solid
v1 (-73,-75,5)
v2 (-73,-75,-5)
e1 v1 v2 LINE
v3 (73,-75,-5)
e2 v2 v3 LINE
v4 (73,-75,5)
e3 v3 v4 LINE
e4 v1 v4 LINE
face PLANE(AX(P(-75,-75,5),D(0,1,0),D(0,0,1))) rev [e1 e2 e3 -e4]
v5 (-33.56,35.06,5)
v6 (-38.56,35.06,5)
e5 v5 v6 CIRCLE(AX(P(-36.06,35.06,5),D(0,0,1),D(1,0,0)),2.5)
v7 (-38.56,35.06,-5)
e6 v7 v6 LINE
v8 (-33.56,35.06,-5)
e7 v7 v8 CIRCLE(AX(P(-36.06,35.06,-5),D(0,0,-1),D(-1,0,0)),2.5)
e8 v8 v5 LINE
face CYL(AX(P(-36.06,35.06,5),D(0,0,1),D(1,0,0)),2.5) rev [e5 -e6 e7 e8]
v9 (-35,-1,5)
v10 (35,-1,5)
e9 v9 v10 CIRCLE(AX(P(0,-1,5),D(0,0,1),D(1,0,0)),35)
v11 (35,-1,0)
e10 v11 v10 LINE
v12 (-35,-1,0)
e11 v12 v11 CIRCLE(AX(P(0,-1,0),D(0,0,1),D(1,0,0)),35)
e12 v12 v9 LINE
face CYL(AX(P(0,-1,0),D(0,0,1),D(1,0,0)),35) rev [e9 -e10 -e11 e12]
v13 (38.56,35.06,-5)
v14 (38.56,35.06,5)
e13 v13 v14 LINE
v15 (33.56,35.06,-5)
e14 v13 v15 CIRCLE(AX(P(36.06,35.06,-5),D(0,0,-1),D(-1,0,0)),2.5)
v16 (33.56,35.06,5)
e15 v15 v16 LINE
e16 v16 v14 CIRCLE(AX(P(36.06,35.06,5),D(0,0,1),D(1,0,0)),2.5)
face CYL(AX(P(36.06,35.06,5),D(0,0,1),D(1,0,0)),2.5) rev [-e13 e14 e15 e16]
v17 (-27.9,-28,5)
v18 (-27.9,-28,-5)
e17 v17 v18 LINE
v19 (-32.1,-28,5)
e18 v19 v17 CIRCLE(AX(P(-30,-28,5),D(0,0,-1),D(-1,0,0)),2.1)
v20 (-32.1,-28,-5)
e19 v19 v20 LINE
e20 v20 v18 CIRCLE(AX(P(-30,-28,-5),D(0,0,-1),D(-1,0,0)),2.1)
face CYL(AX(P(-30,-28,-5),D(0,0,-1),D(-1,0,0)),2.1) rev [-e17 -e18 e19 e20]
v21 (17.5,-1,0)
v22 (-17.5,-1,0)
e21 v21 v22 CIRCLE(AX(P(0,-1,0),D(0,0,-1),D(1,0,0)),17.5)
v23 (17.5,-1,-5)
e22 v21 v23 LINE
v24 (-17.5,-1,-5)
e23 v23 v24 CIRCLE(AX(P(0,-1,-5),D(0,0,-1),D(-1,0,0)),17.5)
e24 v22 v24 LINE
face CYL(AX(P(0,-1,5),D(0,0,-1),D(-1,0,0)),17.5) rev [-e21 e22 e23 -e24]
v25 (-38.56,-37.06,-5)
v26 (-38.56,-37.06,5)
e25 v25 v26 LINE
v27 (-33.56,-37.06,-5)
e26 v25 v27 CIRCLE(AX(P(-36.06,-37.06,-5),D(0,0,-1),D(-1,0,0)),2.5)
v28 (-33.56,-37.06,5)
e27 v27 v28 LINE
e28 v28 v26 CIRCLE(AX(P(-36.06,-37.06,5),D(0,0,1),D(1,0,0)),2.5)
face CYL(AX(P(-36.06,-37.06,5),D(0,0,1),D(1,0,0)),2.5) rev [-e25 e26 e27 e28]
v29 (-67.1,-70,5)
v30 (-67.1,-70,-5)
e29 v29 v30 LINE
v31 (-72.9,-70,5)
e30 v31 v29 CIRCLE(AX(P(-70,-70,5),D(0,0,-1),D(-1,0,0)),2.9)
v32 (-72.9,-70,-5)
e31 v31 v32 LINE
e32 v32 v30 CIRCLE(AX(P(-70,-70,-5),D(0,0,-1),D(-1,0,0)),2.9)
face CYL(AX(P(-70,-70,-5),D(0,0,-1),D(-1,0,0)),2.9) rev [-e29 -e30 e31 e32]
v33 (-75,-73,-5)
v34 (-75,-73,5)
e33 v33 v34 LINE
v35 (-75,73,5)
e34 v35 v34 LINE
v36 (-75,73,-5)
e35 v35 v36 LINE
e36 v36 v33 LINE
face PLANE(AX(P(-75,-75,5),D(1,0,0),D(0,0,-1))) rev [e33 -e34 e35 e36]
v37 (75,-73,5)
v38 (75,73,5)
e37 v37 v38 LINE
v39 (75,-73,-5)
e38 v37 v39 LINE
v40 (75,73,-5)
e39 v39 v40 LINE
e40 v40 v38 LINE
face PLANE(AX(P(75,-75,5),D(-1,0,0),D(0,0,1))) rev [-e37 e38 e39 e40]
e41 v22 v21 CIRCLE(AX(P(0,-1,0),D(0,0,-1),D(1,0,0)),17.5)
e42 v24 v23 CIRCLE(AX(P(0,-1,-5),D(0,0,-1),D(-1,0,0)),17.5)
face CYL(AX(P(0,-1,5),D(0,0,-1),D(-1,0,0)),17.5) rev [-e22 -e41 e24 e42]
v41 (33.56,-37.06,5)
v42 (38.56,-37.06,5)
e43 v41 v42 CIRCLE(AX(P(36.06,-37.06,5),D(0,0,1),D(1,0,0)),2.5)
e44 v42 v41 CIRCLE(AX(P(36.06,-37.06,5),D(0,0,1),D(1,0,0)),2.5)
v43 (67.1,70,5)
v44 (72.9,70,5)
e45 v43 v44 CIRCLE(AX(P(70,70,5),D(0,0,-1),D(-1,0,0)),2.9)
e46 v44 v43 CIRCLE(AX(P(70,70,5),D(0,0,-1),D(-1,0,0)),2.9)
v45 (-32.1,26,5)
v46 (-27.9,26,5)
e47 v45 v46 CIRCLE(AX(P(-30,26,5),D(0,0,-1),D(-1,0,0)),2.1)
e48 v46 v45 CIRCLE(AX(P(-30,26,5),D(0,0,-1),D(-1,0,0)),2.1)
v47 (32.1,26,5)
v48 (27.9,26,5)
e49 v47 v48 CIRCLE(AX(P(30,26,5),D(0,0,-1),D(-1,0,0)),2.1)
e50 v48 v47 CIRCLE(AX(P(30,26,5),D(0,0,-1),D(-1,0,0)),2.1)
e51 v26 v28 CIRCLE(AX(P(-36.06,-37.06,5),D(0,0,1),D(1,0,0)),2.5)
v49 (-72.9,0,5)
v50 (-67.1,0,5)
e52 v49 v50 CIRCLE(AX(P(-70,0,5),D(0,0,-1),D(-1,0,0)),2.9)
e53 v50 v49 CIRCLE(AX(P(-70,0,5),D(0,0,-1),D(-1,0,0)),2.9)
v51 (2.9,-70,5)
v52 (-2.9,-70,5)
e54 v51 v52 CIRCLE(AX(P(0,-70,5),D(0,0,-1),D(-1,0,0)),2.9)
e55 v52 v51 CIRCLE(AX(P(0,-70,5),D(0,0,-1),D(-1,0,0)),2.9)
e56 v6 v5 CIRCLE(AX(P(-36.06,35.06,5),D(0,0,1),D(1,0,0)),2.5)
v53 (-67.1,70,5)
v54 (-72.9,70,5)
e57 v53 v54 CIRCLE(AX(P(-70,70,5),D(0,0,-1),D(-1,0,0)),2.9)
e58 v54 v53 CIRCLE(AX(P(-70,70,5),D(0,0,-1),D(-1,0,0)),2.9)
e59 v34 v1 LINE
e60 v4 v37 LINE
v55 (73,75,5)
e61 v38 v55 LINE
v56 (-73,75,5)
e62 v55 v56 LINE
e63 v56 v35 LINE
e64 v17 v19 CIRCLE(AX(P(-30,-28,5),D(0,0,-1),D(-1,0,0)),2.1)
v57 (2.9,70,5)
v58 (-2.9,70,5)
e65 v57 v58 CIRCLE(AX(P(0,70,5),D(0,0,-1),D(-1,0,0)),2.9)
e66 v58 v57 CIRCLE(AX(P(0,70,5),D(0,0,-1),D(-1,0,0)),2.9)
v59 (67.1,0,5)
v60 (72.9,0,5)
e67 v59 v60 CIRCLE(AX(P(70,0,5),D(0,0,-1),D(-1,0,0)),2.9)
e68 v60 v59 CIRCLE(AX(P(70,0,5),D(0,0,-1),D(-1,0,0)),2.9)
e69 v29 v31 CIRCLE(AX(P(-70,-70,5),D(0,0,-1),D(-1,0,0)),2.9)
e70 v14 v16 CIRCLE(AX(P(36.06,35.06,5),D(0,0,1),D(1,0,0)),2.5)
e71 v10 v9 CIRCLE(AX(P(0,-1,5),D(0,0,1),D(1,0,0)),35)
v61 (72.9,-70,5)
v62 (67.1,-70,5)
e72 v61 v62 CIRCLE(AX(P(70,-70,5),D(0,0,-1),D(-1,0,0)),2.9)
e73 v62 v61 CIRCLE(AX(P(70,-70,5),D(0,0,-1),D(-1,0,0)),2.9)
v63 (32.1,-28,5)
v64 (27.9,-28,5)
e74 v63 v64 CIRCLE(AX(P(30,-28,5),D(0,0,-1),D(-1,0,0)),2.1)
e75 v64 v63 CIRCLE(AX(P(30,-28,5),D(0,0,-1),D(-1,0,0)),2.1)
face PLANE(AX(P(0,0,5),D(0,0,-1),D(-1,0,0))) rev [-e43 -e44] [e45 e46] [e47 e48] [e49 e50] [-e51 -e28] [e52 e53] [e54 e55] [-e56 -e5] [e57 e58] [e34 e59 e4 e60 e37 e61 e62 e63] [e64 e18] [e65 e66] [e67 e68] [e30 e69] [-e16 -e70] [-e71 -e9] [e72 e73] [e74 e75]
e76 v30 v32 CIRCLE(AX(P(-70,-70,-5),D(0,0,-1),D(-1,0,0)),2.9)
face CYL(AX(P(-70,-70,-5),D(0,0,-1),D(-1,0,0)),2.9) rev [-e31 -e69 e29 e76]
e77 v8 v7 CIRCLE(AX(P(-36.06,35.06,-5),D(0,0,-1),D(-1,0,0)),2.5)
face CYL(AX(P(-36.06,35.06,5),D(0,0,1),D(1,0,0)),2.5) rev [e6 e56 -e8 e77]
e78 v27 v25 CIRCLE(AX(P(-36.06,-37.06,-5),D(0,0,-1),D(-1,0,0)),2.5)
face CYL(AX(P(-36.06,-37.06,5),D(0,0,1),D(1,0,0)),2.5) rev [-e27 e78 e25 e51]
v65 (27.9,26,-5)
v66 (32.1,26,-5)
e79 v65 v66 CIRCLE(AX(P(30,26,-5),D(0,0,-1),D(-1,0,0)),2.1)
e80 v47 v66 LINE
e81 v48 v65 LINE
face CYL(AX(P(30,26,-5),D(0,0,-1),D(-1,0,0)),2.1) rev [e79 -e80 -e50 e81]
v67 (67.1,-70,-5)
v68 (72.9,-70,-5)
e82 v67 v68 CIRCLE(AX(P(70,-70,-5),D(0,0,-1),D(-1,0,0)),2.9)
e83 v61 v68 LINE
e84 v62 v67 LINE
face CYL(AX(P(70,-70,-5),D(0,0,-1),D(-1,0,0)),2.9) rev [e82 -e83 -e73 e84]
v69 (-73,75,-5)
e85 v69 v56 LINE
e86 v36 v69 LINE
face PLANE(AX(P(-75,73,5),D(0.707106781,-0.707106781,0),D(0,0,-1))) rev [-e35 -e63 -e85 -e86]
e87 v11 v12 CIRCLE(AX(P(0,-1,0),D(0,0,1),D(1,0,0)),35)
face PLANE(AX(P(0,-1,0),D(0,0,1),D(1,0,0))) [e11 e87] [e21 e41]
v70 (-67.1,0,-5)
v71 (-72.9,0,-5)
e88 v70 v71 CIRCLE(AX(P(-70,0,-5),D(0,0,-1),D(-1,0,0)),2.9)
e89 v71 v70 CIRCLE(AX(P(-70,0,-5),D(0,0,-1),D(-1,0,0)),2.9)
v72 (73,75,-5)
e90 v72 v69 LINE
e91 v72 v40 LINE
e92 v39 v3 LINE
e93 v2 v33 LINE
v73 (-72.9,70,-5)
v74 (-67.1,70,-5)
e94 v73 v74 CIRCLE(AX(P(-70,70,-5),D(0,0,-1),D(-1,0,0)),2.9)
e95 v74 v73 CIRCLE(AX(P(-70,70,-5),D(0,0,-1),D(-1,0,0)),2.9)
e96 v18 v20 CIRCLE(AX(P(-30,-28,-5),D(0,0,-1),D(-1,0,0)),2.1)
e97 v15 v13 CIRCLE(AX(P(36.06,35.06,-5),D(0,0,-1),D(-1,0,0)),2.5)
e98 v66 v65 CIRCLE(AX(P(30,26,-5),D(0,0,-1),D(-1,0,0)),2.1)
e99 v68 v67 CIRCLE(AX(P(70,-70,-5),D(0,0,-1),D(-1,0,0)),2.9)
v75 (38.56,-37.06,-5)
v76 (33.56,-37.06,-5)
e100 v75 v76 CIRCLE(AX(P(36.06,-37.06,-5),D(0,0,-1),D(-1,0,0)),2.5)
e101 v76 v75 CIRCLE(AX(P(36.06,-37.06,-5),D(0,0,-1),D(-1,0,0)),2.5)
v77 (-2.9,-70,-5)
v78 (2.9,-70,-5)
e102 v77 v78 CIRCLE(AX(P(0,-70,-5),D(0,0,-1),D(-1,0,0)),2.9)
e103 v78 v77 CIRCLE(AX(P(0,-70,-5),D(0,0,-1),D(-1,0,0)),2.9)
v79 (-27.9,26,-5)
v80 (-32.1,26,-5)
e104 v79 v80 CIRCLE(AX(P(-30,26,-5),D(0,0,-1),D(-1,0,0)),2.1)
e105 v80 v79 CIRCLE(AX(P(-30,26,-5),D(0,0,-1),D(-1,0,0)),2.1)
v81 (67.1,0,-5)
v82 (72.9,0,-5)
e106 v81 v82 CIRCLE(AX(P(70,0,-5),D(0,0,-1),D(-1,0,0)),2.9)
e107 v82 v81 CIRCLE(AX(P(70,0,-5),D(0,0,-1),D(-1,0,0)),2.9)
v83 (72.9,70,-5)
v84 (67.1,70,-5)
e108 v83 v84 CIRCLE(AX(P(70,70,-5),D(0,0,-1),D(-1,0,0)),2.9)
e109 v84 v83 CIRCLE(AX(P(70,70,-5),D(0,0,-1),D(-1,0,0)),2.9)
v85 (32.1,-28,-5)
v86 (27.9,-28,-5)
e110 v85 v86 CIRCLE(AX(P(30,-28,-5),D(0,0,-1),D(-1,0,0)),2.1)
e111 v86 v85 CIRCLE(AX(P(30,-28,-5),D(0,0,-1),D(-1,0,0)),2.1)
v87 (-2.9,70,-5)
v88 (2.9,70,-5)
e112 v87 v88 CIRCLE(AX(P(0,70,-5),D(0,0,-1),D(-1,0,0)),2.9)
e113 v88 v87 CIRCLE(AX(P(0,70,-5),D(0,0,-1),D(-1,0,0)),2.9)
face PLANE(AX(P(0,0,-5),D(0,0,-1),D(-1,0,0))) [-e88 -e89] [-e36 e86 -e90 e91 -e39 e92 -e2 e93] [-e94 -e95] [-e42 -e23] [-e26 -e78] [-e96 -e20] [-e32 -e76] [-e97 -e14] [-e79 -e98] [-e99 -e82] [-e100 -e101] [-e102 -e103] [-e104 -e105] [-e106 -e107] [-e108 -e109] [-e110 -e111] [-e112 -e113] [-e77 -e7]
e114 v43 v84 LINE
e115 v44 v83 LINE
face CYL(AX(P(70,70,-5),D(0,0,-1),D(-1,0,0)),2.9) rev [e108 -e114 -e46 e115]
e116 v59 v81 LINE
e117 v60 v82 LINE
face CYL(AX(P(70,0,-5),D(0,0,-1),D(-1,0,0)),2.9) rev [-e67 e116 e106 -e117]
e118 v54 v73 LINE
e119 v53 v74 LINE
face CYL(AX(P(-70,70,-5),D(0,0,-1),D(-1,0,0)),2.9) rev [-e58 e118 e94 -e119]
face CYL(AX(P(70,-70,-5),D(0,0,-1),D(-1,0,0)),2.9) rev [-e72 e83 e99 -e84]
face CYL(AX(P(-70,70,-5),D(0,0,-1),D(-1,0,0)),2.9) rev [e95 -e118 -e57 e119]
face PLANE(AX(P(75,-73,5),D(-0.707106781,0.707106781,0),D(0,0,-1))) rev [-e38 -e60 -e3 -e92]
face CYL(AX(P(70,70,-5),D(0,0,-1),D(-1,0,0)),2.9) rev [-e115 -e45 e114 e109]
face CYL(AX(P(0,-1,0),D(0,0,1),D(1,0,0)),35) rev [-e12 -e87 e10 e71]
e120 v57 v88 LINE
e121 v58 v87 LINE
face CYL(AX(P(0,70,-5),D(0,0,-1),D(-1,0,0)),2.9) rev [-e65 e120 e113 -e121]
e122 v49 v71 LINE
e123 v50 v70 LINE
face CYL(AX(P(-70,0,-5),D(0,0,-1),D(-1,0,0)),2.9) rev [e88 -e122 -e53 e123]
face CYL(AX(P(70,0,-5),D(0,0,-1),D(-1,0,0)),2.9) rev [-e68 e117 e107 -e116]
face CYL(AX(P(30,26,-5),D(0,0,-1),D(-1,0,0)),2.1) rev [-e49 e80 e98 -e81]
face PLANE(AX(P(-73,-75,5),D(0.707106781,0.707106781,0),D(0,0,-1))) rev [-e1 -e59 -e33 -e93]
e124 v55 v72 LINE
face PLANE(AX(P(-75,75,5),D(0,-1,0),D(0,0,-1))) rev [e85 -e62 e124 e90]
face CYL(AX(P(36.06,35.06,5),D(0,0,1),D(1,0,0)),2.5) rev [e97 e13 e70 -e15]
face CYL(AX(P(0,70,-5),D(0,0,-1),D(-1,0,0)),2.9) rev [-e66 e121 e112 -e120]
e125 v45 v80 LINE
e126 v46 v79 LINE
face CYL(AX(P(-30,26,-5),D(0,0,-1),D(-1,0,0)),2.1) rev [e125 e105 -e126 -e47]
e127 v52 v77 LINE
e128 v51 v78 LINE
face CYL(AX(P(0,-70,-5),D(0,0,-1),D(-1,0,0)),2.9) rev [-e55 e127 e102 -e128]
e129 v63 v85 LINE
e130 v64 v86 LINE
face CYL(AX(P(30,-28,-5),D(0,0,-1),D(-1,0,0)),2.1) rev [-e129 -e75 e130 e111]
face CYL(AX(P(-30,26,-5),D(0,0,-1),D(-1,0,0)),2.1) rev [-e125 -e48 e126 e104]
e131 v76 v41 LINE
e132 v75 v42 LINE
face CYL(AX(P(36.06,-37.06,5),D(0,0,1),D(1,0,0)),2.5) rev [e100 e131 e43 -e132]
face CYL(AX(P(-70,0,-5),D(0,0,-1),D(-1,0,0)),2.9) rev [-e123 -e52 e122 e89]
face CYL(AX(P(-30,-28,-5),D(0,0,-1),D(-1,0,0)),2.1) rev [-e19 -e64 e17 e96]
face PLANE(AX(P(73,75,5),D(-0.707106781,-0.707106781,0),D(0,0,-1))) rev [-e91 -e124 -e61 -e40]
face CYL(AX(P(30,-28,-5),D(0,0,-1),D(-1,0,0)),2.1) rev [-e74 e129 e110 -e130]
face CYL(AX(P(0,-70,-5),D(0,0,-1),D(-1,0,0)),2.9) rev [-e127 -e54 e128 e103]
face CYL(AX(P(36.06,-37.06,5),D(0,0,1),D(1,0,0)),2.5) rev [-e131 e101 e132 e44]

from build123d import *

# Parameters (mm, degrees)
SKETCH_1_W             = 150
SKETCH_1_H             = 150
EXTRUDE_1_DEPTH        = 5
SKETCH_3_R             = 17.5
CUT_EXTRUDE_1_DEPTH    = 107.536378763
HOLE_WIZARD_M5_1_D     = 5.8
CHAMFER_1_SIZE         = 2
SKETCH_6_R             = 35
CUT_EXTRUDE_2_DEPTH    = 5
HOLE_WIZARD_M6_1_D     = 5
HOLE_WIZARD_M6_1_DEPTH = 10
HOLE_WIZARD_M5_1_2_D   = 4.2


with BuildPart() as part:
    # 草图1 → 凸台-拉伸1 (new, symmetric)
    with BuildSketch(Plane.XY):
        Rectangle(SKETCH_1_W, SKETCH_1_H)
    extrude(amount=EXTRUDE_1_DEPTH, both=True)

    # 草图3 → 切除-拉伸1 (cut, through all)
    with BuildSketch(Plane(origin=(0, 0, -5), x_dir=(-1, 0, 0), z_dir=(0, 0, -1))):
        with Locations((0, -1)):
            Circle(SKETCH_3_R)
    extrude(amount=-CUT_EXTRUDE_1_DEPTH, mode=Mode.SUBTRACT)

    # Hole Wizard M5 _1 (through all)
    with Locations(Plane(origin=(0, 0, -5), x_dir=(-1, 0, 0), z_dir=(0, 0, -1))):
        with Locations((-70, 70), (-70, 0), (-70, -70), (0, -70), (70, -70), (70, 0), (70, 70), (0, 70)):
            Hole(HOLE_WIZARD_M5_1_D / 2)

    # 倒角1
    chamfer_1_edges = [part.edges().sort_by_distance(p)[0] for p in [
        (75, -75, 0),
        (-75, -75, 0),
        (-75, 75, 0),
        (75, 75, 0),
    ]]
    chamfer(chamfer_1_edges, length=CHAMFER_1_SIZE)

    # 草图6 → 切除-拉伸2 (cut)
    with BuildSketch(Plane.XY.offset(5)):
        with Locations((0, -1)):
            Circle(SKETCH_6_R)
    extrude(amount=-CUT_EXTRUDE_2_DEPTH, mode=Mode.SUBTRACT)

    # M6 螺纹孔1
    with Locations(Plane.XY.offset(5)):
        with Locations((-36.06, 35.06), (0, -1), (36.06, -37.06), (36.06, 35.06), (-36.06, -37.06)):
            Hole(HOLE_WIZARD_M6_1_D / 2, depth=HOLE_WIZARD_M6_1_DEPTH)

    # Hole Wizard M5 _1 2 (through all)
    with Locations(Plane(origin=(0, 0, -5), x_dir=(-1, 0, 0), z_dir=(0, 0, -1))):
        with Locations((-30, 26), (30, 26), (-30, -28), (30, -28)):
            Hole(HOLE_WIZARD_M5_1_2_D / 2)


solid = part.part
